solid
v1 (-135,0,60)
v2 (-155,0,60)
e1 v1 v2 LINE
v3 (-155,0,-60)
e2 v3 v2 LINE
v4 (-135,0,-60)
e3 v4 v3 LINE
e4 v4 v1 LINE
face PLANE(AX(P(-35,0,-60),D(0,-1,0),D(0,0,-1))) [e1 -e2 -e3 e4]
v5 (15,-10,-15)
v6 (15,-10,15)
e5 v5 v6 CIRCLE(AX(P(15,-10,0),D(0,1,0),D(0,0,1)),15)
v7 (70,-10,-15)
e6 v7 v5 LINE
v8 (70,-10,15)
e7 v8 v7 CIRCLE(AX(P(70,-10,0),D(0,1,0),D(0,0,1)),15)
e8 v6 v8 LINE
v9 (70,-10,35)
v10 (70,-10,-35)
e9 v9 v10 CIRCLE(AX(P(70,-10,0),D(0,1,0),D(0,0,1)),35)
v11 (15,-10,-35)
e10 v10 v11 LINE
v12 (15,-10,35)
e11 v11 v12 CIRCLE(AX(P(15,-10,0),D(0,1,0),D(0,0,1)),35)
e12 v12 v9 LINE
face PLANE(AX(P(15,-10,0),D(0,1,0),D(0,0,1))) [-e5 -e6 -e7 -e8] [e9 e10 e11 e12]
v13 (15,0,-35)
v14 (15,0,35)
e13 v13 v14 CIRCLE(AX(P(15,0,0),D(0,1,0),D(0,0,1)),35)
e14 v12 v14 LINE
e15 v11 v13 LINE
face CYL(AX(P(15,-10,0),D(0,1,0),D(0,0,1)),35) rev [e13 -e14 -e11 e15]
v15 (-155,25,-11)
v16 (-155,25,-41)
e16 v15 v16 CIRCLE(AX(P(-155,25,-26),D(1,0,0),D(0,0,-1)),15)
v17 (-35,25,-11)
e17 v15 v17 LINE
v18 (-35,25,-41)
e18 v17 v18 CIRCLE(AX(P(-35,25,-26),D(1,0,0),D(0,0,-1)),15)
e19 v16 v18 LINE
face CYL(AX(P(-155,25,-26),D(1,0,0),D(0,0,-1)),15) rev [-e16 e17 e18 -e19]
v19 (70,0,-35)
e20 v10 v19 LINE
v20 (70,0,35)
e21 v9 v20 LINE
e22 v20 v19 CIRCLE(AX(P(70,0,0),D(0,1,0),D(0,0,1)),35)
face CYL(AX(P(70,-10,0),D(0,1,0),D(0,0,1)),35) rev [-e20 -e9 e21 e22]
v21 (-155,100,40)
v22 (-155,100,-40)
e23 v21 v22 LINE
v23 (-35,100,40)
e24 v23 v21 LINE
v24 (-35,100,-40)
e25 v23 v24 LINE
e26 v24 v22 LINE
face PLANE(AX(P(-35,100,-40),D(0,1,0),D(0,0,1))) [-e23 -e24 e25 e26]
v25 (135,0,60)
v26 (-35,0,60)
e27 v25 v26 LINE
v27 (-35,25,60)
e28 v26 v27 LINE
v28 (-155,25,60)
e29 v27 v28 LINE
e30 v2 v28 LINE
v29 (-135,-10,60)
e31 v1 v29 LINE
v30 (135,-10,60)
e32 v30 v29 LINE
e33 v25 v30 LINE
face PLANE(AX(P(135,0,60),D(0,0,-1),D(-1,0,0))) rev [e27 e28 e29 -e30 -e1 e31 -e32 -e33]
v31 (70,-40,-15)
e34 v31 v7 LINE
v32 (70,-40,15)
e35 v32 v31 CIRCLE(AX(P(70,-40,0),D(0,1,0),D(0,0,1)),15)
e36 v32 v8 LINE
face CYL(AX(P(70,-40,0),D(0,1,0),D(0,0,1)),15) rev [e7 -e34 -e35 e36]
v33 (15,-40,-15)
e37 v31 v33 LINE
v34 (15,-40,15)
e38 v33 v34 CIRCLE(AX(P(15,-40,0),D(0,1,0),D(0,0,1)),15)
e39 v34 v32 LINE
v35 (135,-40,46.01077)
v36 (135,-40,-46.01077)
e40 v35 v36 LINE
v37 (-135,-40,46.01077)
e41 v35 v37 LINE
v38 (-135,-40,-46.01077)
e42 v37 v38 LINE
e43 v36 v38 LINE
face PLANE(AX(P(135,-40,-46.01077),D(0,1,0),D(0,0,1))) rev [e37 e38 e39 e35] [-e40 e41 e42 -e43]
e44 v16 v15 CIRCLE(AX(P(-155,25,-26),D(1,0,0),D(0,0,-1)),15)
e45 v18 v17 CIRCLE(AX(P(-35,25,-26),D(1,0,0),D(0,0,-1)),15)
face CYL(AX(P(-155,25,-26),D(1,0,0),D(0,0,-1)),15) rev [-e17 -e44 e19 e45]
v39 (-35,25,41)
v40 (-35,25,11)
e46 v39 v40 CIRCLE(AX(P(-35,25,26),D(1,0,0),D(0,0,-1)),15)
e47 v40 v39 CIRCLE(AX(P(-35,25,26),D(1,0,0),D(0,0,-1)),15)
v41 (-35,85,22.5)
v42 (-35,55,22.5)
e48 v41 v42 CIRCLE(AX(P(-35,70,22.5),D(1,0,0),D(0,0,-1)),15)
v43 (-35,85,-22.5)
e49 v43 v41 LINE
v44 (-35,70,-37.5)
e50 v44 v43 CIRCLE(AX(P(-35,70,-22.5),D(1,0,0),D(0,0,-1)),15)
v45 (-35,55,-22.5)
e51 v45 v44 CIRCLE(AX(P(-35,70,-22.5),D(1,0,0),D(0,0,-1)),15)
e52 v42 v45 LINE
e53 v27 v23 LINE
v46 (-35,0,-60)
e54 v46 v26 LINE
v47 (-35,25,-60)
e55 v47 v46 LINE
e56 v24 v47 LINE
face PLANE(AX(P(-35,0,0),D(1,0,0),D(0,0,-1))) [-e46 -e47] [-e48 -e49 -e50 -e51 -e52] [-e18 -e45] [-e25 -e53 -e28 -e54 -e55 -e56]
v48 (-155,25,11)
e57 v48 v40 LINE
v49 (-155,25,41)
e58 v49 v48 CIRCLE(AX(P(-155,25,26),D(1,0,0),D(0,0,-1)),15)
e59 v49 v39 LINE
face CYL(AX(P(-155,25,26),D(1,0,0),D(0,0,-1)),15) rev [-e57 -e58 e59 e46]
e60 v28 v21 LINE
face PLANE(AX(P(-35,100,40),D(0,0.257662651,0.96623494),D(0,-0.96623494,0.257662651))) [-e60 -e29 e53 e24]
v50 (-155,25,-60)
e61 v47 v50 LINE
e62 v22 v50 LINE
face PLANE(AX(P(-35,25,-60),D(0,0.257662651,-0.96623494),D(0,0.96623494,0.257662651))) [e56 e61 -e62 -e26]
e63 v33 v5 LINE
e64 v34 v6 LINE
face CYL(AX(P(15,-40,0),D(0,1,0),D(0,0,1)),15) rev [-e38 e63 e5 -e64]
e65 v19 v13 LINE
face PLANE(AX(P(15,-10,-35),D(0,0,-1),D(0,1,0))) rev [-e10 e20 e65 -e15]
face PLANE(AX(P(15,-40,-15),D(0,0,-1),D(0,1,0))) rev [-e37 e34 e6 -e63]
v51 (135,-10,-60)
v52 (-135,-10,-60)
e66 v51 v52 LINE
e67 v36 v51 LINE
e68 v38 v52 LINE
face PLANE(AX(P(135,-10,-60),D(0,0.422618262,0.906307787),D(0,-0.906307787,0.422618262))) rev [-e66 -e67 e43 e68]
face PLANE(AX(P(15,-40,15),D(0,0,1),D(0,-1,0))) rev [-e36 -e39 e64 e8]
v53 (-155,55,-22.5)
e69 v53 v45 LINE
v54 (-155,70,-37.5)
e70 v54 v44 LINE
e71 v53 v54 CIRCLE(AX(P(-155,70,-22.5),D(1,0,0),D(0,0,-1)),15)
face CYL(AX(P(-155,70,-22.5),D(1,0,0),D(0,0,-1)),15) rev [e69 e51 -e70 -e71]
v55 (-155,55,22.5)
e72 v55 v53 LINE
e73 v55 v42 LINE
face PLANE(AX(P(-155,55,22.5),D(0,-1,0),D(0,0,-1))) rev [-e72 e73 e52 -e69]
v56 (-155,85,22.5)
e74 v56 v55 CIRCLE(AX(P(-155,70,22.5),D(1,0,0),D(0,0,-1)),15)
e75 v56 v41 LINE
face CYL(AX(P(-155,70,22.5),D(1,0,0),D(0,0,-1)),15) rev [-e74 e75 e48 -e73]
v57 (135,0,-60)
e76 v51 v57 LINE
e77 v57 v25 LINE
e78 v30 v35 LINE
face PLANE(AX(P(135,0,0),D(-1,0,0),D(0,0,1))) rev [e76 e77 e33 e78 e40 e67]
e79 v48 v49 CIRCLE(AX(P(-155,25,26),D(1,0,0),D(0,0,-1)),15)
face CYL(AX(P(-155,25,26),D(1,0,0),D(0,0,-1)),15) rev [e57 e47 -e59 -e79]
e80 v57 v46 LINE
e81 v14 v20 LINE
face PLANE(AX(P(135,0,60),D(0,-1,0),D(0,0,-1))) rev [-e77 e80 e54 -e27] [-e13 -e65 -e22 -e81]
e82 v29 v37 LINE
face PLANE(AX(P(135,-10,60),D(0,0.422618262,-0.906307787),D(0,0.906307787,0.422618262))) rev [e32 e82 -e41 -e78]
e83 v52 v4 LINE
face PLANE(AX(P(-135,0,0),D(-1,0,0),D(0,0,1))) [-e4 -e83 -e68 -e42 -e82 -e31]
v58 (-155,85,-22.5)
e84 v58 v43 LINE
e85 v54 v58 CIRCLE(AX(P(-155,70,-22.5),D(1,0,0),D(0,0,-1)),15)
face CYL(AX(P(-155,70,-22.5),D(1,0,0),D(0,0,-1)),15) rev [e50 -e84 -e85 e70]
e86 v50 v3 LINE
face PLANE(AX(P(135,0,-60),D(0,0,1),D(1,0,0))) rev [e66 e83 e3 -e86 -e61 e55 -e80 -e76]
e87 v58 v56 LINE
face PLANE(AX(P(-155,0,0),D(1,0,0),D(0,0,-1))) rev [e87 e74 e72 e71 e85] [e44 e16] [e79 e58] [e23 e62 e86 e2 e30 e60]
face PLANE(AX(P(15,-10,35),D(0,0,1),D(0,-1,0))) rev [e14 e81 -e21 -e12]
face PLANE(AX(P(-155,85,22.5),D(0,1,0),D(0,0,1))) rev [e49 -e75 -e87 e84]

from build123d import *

# Parameters (mm, degrees)
WEDGE_BASE_RAIL_DEPTH         = 135
UPRIGHT_START                 = 20
UPRIGHT_BLOCK_DEPTH           = 120
BLOCK_SLOT_AND_HOLES_SKETCH_R = 15
BLOCK_SLOT_AND_HOLES_2X_DEPTH = 120
SLOT_COUNTERBORE_POCKET_DEPTH = 10
ADJUSTMENT_SLOT_THROUGH_DEPTH = 200.31131428


with BuildPart() as part:
    # Wedge Rail Profile Sketch → Wedge Base Rail (new, symmetric)
    with BuildSketch(Plane(origin=(0, 0, 0), x_dir=(0, 0, -1), z_dir=(1, 0, 0))):
        Polygon((-60, 0), (60, 0), (60, -10), (46.010770255, -40), (-46.010770255, -40), (-60, -10), align=None)
    extrude(amount=WEDGE_BASE_RAIL_DEPTH, both=True)

    # Upright Block Sketch → Upright Block (add)
    with BuildSketch(Plane.ZY.offset(135).offset(UPRIGHT_START)):
        Polygon((-60, 0), (-60, 25), (-40, 100), (40, 100), (60, 25), (60, 0), align=None)
    extrude(amount=-UPRIGHT_BLOCK_DEPTH)

    # Block Slot and Holes Sketch → Block Slot and Holes 2x (cut)
    with BuildSketch(Plane(origin=(-35, 0, 0), x_dir=(0, 0, -1), z_dir=(1, 0, 0))):
        with Locations((-26, 25)):
            Circle(BLOCK_SLOT_AND_HOLES_SKETCH_R)
        with Locations((26, 25)):
            Circle(BLOCK_SLOT_AND_HOLES_SKETCH_R)
        with BuildLine():
            Line((-22.5, 85), (22.5, 85))
            ThreePointArc((22.5, 85), (37.5, 70), (22.5, 55))
            Line((22.5, 55), (-22.5, 55))
            ThreePointArc((-22.5, 55), (-37.5, 70), (-22.5, 85))
        make_face()
    extrude(amount=-BLOCK_SLOT_AND_HOLES_2X_DEPTH, mode=Mode.SUBTRACT)

    # Slot Counterbore Sketch → Slot Counterbore Pocket (cut)
    with BuildSketch(Plane(origin=(0, 0, 0), x_dir=(1, 0, 0), z_dir=(0, 1, 0))):
        with BuildLine():
            Line((15, 35), (70, 35))
            ThreePointArc((70, 35), (105, 0), (70, -35))
            Line((70, -35), (15, -35))
            ThreePointArc((15, -35), (-20, 0), (15, 35))
        make_face()
    extrude(amount=-SLOT_COUNTERBORE_POCKET_DEPTH, mode=Mode.SUBTRACT)

    # Adjustment Slot Sketch → Adjustment Slot Through (cut, through all)
    with BuildSketch(Plane(origin=(0, -10, 0), x_dir=(1, 0, 0), z_dir=(0, 1, 0))):
        with BuildLine():
            Line((15, 15), (70, 15))
            ThreePointArc((70, 15), (85, 0), (70, -15))
            Line((70, -15), (15, -15))
            ThreePointArc((15, -15), (0, 0), (15, 15))
        make_face()
    extrude(amount=-ADJUSTMENT_SLOT_THROUGH_DEPTH, mode=Mode.SUBTRACT)


solid = part.part
